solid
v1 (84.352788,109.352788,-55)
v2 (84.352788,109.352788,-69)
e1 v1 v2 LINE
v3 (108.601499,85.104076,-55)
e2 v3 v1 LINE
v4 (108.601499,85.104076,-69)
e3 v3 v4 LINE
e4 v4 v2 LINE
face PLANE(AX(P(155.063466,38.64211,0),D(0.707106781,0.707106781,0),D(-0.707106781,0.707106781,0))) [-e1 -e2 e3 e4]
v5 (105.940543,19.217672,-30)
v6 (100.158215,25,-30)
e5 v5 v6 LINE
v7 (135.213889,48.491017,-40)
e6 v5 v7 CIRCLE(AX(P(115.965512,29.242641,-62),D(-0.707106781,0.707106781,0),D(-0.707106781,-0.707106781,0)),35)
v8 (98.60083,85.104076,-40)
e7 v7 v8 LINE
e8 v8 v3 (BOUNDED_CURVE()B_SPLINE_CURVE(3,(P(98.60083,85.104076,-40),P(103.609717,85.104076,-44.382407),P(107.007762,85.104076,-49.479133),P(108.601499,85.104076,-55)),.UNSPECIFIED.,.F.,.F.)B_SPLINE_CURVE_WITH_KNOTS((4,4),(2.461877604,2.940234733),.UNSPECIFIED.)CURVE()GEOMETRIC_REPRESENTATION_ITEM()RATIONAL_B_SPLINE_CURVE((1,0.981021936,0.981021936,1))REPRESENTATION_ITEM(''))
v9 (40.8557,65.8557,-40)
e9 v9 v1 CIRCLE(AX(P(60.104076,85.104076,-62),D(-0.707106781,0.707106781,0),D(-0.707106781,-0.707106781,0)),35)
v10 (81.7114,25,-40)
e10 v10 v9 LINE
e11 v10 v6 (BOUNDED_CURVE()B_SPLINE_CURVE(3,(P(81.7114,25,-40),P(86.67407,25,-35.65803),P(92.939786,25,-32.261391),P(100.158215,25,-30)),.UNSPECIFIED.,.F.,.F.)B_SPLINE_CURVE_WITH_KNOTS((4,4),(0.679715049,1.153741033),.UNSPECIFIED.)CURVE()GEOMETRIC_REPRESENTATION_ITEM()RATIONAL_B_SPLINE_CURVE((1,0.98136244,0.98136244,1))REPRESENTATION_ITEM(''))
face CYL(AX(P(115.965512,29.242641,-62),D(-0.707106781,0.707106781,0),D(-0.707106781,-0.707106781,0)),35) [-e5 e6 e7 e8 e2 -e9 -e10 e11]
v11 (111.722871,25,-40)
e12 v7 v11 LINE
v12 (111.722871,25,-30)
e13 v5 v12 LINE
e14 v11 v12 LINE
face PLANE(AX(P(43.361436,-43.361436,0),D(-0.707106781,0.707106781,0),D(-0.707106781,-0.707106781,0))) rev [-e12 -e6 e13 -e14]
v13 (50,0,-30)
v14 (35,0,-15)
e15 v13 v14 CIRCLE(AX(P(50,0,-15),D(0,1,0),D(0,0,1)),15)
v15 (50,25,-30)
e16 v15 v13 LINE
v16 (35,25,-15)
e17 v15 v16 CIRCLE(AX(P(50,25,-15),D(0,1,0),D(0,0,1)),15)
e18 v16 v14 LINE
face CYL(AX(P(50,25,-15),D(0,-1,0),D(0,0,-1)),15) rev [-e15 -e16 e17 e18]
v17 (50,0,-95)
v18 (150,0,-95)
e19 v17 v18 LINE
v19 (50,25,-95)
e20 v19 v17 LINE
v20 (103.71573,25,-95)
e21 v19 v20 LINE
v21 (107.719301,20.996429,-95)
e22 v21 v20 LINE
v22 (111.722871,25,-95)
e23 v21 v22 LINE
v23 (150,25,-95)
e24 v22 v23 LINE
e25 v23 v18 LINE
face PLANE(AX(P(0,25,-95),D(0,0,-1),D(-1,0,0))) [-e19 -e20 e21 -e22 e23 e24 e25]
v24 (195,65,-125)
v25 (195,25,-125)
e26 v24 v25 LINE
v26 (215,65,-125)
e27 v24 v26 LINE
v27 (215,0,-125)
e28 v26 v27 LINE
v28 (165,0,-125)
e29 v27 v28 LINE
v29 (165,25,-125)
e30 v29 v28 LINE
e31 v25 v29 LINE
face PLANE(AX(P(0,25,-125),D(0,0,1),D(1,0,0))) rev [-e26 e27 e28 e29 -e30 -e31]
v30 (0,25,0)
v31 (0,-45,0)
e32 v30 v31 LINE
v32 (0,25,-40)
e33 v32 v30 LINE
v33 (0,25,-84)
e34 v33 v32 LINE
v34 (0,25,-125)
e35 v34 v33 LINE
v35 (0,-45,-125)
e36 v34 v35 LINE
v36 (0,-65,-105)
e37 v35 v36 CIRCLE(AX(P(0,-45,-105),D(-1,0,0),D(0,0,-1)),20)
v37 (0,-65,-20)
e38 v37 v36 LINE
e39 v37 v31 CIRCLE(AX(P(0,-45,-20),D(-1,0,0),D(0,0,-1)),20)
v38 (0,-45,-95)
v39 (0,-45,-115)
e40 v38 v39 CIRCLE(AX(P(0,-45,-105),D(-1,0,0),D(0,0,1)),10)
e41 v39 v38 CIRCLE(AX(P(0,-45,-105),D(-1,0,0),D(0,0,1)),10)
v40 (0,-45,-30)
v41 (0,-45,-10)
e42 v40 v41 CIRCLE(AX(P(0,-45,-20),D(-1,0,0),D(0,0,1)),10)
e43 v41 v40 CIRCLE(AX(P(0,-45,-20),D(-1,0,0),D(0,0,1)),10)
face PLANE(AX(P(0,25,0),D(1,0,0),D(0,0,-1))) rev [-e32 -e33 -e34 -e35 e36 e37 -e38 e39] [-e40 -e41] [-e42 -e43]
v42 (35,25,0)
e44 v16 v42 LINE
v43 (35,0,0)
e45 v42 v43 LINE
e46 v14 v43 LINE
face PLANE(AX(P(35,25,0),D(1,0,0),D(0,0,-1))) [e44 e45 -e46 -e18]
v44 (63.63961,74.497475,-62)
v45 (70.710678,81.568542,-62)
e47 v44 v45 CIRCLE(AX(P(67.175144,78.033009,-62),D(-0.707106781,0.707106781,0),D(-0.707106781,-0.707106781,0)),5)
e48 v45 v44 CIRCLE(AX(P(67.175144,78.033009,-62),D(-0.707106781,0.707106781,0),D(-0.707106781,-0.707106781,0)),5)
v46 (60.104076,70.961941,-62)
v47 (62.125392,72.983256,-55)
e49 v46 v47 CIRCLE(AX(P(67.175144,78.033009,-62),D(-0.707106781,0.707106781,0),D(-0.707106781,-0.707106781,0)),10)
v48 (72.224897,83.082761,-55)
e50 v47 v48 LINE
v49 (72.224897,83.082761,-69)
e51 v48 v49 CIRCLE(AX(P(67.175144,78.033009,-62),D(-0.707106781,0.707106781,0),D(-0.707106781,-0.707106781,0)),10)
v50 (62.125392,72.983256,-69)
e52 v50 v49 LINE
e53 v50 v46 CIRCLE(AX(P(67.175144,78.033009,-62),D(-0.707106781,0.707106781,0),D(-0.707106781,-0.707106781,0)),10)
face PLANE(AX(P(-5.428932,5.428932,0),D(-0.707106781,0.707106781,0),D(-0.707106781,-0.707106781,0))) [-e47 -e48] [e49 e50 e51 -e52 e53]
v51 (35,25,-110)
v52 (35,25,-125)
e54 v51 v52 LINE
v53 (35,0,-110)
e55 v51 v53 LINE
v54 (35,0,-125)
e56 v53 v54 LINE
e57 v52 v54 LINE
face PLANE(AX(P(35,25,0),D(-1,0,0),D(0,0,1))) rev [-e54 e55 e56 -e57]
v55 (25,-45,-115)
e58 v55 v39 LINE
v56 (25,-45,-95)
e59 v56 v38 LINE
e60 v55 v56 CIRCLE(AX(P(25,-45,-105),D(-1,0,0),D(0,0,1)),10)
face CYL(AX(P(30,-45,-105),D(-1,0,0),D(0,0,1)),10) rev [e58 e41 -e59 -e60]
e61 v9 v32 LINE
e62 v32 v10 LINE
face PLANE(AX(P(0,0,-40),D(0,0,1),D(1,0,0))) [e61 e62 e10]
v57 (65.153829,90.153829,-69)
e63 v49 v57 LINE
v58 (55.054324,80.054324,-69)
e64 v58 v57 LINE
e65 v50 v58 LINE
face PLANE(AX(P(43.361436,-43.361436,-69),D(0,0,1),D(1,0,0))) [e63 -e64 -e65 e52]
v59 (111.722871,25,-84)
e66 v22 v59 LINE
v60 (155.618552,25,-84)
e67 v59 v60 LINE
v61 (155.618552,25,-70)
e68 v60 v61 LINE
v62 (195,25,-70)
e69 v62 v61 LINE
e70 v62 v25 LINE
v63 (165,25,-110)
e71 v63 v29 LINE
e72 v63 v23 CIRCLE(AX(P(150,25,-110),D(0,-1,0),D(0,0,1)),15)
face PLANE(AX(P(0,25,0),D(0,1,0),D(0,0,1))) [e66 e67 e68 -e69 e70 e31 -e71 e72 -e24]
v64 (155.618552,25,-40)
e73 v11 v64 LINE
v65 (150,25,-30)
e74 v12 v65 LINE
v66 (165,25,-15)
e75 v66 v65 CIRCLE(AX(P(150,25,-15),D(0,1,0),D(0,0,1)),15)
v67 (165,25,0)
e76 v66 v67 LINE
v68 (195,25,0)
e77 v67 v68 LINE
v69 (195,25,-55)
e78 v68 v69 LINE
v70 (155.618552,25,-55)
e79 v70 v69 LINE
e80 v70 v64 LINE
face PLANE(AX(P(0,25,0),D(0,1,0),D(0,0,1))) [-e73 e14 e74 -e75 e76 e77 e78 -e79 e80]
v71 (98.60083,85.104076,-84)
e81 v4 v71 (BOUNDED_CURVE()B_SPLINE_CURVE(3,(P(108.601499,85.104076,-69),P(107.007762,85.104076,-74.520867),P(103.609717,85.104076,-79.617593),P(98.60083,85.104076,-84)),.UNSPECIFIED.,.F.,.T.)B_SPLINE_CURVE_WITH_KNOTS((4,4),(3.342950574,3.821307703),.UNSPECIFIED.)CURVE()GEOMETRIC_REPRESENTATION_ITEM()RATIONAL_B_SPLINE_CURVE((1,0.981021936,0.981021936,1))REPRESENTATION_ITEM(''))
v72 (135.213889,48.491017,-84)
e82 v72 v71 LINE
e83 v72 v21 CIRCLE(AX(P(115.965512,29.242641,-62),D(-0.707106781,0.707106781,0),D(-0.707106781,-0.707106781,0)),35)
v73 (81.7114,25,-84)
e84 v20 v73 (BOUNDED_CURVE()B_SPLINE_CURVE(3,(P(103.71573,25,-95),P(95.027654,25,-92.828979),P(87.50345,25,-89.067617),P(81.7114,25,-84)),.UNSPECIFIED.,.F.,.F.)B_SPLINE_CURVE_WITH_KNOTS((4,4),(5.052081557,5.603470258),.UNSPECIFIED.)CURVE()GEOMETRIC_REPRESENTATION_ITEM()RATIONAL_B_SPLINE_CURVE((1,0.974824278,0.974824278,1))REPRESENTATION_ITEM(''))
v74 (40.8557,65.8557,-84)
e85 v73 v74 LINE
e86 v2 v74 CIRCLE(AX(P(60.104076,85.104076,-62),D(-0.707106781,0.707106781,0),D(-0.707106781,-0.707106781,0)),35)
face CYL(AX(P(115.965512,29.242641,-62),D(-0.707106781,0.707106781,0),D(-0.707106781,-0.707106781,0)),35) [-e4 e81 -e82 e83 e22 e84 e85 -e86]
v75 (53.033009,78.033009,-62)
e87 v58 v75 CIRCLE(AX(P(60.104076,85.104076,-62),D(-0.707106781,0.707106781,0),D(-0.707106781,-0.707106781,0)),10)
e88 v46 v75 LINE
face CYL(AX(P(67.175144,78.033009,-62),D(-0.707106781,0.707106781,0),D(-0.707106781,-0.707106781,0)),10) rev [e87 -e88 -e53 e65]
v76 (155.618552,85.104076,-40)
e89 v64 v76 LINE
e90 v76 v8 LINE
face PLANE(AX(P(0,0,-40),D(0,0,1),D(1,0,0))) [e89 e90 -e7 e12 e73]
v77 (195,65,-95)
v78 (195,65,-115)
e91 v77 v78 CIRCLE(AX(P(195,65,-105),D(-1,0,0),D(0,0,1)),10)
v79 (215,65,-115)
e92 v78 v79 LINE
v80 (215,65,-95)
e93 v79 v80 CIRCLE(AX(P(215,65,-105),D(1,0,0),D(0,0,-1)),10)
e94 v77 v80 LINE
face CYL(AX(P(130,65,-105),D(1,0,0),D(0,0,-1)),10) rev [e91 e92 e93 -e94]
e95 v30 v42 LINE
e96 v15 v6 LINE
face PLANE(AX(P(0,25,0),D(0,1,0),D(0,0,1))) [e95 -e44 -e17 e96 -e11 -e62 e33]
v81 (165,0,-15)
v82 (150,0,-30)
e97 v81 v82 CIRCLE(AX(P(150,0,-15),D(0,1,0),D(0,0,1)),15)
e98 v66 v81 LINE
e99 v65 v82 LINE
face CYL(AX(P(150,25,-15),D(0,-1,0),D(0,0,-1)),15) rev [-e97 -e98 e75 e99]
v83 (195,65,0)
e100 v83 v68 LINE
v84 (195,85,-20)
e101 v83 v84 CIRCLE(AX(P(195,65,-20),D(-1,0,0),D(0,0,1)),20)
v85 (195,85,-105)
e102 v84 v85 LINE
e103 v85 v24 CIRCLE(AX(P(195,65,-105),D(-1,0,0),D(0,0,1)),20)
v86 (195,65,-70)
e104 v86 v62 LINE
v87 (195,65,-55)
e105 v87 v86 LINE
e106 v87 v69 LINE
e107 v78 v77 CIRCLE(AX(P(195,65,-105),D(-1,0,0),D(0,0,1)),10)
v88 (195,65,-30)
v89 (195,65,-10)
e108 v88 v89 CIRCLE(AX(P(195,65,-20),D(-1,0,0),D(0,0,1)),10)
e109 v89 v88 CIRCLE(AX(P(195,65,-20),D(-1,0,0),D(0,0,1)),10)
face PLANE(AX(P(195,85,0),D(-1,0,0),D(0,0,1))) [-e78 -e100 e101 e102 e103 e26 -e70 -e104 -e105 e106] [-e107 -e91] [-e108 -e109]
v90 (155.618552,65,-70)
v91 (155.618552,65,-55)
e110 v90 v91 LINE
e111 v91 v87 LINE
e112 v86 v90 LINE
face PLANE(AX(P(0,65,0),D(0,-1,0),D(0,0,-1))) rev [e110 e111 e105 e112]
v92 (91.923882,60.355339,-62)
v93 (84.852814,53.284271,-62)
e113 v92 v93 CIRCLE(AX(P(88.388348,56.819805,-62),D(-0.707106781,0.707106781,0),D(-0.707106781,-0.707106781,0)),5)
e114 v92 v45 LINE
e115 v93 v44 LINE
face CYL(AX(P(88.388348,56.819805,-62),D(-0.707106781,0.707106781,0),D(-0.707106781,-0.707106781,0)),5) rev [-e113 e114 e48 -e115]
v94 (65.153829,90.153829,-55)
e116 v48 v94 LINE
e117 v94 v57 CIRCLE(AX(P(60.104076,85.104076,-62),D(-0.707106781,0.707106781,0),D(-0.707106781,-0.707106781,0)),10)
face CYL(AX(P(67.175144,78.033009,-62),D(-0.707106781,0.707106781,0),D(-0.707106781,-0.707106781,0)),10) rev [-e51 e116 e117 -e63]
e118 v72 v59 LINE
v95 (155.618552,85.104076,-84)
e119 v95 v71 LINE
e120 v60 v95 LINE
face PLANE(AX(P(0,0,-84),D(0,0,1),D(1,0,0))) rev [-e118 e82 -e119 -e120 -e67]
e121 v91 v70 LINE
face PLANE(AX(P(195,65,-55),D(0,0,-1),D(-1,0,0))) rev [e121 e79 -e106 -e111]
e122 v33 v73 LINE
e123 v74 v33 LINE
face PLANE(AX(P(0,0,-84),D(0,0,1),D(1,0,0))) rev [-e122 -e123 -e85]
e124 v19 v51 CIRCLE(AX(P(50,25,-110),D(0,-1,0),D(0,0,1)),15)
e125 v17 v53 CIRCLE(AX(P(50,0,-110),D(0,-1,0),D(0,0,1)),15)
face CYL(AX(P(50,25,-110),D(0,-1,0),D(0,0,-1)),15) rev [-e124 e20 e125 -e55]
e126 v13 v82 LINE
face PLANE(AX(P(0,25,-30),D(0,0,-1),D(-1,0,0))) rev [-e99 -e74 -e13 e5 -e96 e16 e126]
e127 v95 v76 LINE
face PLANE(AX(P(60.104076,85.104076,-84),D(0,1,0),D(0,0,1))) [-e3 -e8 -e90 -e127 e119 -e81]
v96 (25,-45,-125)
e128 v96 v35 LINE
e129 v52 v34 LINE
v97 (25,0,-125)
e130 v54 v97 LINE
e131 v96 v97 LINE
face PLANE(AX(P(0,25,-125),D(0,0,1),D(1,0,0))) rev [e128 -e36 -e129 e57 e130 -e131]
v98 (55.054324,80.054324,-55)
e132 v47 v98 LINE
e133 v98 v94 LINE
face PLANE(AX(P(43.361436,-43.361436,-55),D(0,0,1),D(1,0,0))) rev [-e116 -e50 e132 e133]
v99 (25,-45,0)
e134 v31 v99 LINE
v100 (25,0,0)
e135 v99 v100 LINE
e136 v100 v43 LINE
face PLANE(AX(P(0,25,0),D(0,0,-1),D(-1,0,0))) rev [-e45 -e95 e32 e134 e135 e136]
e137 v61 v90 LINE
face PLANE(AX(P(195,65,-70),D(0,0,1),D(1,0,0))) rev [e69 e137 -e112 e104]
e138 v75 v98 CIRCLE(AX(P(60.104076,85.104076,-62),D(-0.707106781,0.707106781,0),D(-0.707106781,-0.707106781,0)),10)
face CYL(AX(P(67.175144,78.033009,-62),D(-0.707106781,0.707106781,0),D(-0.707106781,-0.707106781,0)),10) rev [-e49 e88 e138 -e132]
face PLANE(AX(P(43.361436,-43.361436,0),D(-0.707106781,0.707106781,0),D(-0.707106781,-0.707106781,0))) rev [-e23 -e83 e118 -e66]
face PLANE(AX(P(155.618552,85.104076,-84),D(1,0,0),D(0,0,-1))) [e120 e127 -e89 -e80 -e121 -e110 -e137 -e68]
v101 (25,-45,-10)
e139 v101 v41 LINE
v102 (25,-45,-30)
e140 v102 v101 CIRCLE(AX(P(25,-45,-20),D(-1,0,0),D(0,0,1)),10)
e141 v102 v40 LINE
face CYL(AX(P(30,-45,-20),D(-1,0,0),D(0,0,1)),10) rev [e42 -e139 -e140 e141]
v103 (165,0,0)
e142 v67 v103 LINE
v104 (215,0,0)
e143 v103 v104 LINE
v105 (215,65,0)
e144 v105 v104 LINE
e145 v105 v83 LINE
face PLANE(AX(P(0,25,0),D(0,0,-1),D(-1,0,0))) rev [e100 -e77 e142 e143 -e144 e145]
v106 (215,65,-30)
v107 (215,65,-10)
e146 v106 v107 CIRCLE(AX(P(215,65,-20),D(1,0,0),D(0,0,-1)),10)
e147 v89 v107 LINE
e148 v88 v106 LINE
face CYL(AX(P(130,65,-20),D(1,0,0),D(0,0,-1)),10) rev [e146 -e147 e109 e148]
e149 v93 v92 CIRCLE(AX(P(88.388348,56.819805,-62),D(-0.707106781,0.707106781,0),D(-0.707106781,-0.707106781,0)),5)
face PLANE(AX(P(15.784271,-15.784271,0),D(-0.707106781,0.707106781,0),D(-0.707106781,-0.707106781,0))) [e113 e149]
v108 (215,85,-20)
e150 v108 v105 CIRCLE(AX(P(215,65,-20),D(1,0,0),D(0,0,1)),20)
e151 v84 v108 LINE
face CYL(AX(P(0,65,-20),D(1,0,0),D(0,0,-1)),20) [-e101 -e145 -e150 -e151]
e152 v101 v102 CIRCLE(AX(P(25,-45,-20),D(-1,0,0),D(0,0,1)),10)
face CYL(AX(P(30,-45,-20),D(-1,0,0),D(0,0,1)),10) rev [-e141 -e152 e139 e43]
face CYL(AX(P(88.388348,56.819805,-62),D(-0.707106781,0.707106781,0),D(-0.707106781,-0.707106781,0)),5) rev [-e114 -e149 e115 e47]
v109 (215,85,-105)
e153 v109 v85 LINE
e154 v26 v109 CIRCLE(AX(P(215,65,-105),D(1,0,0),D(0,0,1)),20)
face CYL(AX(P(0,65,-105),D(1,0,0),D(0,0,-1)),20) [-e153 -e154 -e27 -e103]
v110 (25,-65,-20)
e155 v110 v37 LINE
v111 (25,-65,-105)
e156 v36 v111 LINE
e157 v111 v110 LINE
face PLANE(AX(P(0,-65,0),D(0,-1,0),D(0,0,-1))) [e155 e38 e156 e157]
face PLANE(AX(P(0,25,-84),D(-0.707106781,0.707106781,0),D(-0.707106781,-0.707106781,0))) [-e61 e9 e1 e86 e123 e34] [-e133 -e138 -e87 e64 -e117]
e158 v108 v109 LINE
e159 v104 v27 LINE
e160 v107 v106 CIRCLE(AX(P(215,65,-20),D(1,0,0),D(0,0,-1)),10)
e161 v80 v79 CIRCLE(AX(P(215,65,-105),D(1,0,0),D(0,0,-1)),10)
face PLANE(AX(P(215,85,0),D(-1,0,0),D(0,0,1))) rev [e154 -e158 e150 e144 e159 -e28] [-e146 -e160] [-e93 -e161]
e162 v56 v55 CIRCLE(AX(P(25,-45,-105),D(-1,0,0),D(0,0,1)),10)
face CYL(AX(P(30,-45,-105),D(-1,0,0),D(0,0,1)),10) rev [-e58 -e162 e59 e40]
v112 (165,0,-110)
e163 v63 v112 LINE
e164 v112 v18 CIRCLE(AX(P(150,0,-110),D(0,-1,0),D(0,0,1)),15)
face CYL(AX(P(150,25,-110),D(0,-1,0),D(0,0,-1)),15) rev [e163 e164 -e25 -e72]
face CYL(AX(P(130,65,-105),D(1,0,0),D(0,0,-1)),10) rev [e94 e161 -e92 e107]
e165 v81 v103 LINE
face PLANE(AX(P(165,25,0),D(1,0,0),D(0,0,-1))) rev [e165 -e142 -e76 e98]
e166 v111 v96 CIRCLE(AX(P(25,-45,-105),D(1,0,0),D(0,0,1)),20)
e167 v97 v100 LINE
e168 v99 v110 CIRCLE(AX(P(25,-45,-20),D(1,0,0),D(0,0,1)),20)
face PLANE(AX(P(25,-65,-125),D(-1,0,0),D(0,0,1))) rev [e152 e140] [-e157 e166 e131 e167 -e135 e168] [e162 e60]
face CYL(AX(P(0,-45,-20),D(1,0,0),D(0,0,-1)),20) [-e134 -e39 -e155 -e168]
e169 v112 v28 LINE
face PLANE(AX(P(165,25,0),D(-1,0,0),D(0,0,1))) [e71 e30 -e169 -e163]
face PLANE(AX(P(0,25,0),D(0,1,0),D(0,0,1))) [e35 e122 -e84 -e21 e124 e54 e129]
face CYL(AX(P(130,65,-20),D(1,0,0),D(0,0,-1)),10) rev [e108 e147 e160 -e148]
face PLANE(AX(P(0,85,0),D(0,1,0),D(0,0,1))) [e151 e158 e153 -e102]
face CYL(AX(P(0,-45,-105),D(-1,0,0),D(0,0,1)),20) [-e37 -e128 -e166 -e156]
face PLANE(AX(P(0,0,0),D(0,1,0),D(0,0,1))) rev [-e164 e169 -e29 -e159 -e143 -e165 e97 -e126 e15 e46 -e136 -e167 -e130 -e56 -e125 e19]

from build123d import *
from build123d.topology import SkipClean

# Parameters (mm, degrees)
BASE_PLATE_DEPTH               = 25
SKETCH1_3_W                    = 20
SKETCH1_3_H                    = 62.5
UPRIGHT_FLANGE_DEPTH           = 85
UPRIGHT_FLANGE_FILLET_R20_R    = 20
FLANGE_HOLES_SKETCH_R          = 10
FLANGE_MOUNTING_HOLES_2X_DEPTH = 85
CONNECTING_WEB_SKETCH_W        = 40
CONNECTING_WEB_SKETCH_H        = 15
CONNECTING_WEB_DEPTH           = 40
SIDE_LUG_SKETCH_W              = 25
SIDE_LUG_SKETCH_H              = 125
SIDE_LUG_DEPTH                 = 65
SIDE_LUG_FILLET_R20_R          = 20
LUG_HOLES_SKETCH_R             = 10
LUG_MOUNTING_HOLES_2X_DEPTH    = 30
BEARING_BLOCK_DEPTH            = 44
BLOCK_SLOT_SKETCH_R            = 5
BLOCK_SLOT_CUT_44_DEPTH        = 44
SKETCH12_4_R                   = 10
SKETCH12_4_R_2                 = 5
BLOCK_SLOT_CUT_10_A_DEPTH      = 10
GUIDE_BAR_SKETCH_W             = 14
GUIDE_BAR_SKETCH_H             = 44.292856399
GUIDE_BAR_100_DEPTH            = 100
SKETCH12_5_R                   = 5
BLOCK_SLOT_CUT_40_DEPTH        = 40
SKETCH12_6_R                   = 10
SKETCH12_6_R_2                 = 5
BLOCK_SLOT_CUT_10_B_DEPTH      = 10
GUIDE_BAR_79_DEPTH             = 79


with BuildPart() as part:
    # Base Profile Sketch → Base Plate (new body)
    with BuildSketch(Plane(origin=(0, 0, 0), x_dir=(1, 0, 0), z_dir=(0, 1, 0))):
        with BuildLine():
            Line((0, 62.5), (0, 0))
            Line((0, 0), (35, 0))
            Line((35, 0), (35, 15))
            ThreePointArc((35, 15), (39.393398282, 25.606601718), (50, 30))
            Line((50, 30), (150, 30))
            ThreePointArc((150, 30), (160.606601718, 25.606601718), (165, 15))
            Line((165, 15), (165, 0))
            Line((165, 0), (195, 0))
            Line((195, 0), (195, 62.5))
            Line((195, 62.5), (0, 62.5))
        make_face()
        with BuildLine():
            Line((0, 125), (0, 62.5))
            Line((0, 62.5), (195, 62.5))
            Line((195, 62.5), (195, 125))
            Line((195, 125), (165, 125))
            Line((165, 125), (165, 110))
            ThreePointArc((165, 110), (160.606601718, 99.393398282), (150, 95))
            Line((150, 95), (50, 95))
            ThreePointArc((50, 95), (39.393398282, 99.393398282), (35, 110))
            Line((35, 110), (35, 125))
            Line((35, 125), (0, 125))
        make_face()
    extrude(amount=BASE_PLATE_DEPTH)

    # Sketch1_3 → Upright Flange (add)
    with BuildSketch(Plane(origin=(0, 0, 0), x_dir=(1, 0, 0), z_dir=(0, 1, 0))):
        with Locations((205, 31.25)):
            Rectangle(SKETCH1_3_W, SKETCH1_3_H)
        with Locations((205, 93.75)):
            Rectangle(SKETCH1_3_W, SKETCH1_3_H)
    extrude(amount=UPRIGHT_FLANGE_DEPTH)

    # Upright Flange Fillet R20
    upright_flange_fillet_r20_edges = [part.edges().sort_by_distance(p)[0] for p in [
        (205, 85, 0),
        (205, 85, -125),
    ]]
    fillet(upright_flange_fillet_r20_edges, radius=UPRIGHT_FLANGE_FILLET_R20_R)

    # Flange Holes Sketch → Flange Mounting Holes 2x (cut)
    with BuildSketch(Plane(origin=(215, 0, 0), x_dir=(0, 0, -1), z_dir=(1, 0, 0))):
        with Locations((20, 65)):
            Circle(FLANGE_HOLES_SKETCH_R)
        with Locations((105, 65)):
            Circle(FLANGE_HOLES_SKETCH_R)
    extrude(amount=-FLANGE_MOUNTING_HOLES_2X_DEPTH, mode=Mode.SUBTRACT)

    # Connecting Web Sketch → Connecting Web (add)
    with BuildSketch(Plane(origin=(0, 25, 0), x_dir=(1, 0, 0), z_dir=(0, 1, 0))):
        with Locations((175, 62.5)):
            Rectangle(CONNECTING_WEB_SKETCH_W, CONNECTING_WEB_SKETCH_H)
    extrude(amount=CONNECTING_WEB_DEPTH)

    # Side Lug Sketch → Side Lug (add)
    with BuildSketch(Plane(origin=(0, 0, 0), x_dir=(-1, 0, 0), z_dir=(0, -1, 0))):
        with Locations((-12.5, 62.5)):
            Rectangle(SIDE_LUG_SKETCH_W, SIDE_LUG_SKETCH_H)
    extrude(amount=SIDE_LUG_DEPTH)

    # Side Lug Fillet R20
    side_lug_fillet_r20_edges = [part.edges().sort_by_distance(p)[0] for p in [
        (12.5, -65, 0),
        (12.5, -65, -125),
    ]]
    fillet(side_lug_fillet_r20_edges, radius=SIDE_LUG_FILLET_R20_R)

    # Lug Holes Sketch → Lug Mounting Holes 2x (cut)
    with BuildSketch(Plane.ZY):
        with Locations((-105, -45)):
            Circle(LUG_HOLES_SKETCH_R)
        with Locations((-20, -45)):
            Circle(LUG_HOLES_SKETCH_R)
    extrude(amount=-LUG_MOUNTING_HOLES_2X_DEPTH, mode=Mode.SUBTRACT)

    # Bearing Block Profile Sketch → Bearing Block (add)
    with BuildSketch(Plane.XY.offset(-40)):
        Polygon((0, 25), (60.104076401, 85.104076401), (146.293439814, 85.104076401), (155.618552468, 85.104076401), (155.618552468, 76.954753414), (155.618552468, 25), align=None)
    extrude(amount=-BEARING_BLOCK_DEPTH)

    # Block Slot Sketch → Block Slot Cut 44 (cut)
    with BuildSketch(Plane(origin=(-12.5, 12.5, 0), x_dir=(0, 0, 1), z_dir=(-0.7071067811865488, 0.7071067811865464, 0))):
        with Locations(Location((-62, 102.67766953, 0), (0, 0, 270))):
            Circle(BLOCK_SLOT_SKETCH_R)
    extrude(amount=-BLOCK_SLOT_CUT_44_DEPTH, mode=Mode.SUBTRACT)

    # Sketch12_4 → Block Slot Cut 10 A (cut)
    with SkipClean():  # the faces are left unmerged after this step: merging them gives an invalid solid
        with BuildSketch(Plane(origin=(-12.5, 12.5, 0), x_dir=(0, 0, 1), z_dir=(-0.7071067811865488, 0.7071067811865464, 0))):
            with Locations((-62, 102.67766953)):
                Circle(SKETCH12_4_R)
            with Locations((-62, 102.67766953)):
                Circle(SKETCH12_4_R_2, mode=Mode.SUBTRACT)
        extrude(amount=-BLOCK_SLOT_CUT_10_A_DEPTH, mode=Mode.SUBTRACT)

    # Guide Bar Sketch → Guide Bar 100 (add)
    with BuildSketch(Plane(origin=(-12.5, 12.5, 0), x_dir=(0, 0, 1), z_dir=(-0.7071067811865488, 0.7071067811865464, 0))):
        with Locations((-62, 114.82409773)):
            Rectangle(GUIDE_BAR_SKETCH_W, GUIDE_BAR_SKETCH_H)
    extrude(amount=-GUIDE_BAR_100_DEPTH)

    # Sketch12_5 → Block Slot Cut 40 (cut)
    with BuildSketch(Plane(origin=(-12.5, 12.5, 0), x_dir=(0, 0, 1), z_dir=(-0.7071067811865488, 0.7071067811865464, 0))):
        with Locations(Location((-62, 102.67766953, 0), (0, 0, 270))):
            Circle(SKETCH12_5_R)
    extrude(amount=-BLOCK_SLOT_CUT_40_DEPTH, mode=Mode.SUBTRACT)

    # Sketch12_6 → Block Slot Cut 10 B (cut)
    with BuildSketch(Plane(origin=(-12.5, 12.5, 0), x_dir=(0, 0, 1), z_dir=(-0.7071067811865488, 0.7071067811865464, 0))):
        with Locations(Location((-62, 102.67766953, 0), (0, 0, 270))):
            Circle(SKETCH12_6_R)
        with Locations(Location((-62, 102.67766953, 0), (0, 0, 270))):
            Circle(SKETCH12_6_R_2, mode=Mode.SUBTRACT)
    extrude(amount=-BLOCK_SLOT_CUT_10_B_DEPTH, mode=Mode.SUBTRACT)

    # Sketch13_6 → Guide Bar 79 (add)
    with BuildSketch(Plane(origin=(-12.5, 12.5, 0), x_dir=(0, 0, 1), z_dir=(-0.7071067811865488, 0.7071067811865464, 0))):
        with BuildLine():
            Line((-55, 136.970525929), (-55, 95.536241101))
            ThreePointArc((-55, 95.536241101), (-52.780455543, 98.804686183), (-52, 102.67766953))
            Line((-52, 102.67766953), (-40, 102.67766953))
            Line((-40, 102.67766953), (-40, 75.456354352))
            ThreePointArc((-40, 75.456354352), (-30.416776605, 87.594566401), (-27, 102.67766953))
            ThreePointArc((-27, 102.67766953), (-34.889116577, 124.813613151), (-55, 136.970525929))
        make_face()
        with BuildLine():
            ThreePointArc((-72, 102.67766953), (-71.219544457, 98.804686183), (-69, 95.536241101))
            Line((-69, 95.536241101), (-69, 136.970525929))
            ThreePointArc((-69, 136.970525929), (-96.00365166, 110.96933244), (-84, 75.456354352))
            Line((-84, 75.456354352), (-84, 102.67766953))
            Line((-84, 102.67766953), (-72, 102.67766953))
        make_face()
    extrude(amount=-GUIDE_BAR_79_DEPTH)


solid = part.part
